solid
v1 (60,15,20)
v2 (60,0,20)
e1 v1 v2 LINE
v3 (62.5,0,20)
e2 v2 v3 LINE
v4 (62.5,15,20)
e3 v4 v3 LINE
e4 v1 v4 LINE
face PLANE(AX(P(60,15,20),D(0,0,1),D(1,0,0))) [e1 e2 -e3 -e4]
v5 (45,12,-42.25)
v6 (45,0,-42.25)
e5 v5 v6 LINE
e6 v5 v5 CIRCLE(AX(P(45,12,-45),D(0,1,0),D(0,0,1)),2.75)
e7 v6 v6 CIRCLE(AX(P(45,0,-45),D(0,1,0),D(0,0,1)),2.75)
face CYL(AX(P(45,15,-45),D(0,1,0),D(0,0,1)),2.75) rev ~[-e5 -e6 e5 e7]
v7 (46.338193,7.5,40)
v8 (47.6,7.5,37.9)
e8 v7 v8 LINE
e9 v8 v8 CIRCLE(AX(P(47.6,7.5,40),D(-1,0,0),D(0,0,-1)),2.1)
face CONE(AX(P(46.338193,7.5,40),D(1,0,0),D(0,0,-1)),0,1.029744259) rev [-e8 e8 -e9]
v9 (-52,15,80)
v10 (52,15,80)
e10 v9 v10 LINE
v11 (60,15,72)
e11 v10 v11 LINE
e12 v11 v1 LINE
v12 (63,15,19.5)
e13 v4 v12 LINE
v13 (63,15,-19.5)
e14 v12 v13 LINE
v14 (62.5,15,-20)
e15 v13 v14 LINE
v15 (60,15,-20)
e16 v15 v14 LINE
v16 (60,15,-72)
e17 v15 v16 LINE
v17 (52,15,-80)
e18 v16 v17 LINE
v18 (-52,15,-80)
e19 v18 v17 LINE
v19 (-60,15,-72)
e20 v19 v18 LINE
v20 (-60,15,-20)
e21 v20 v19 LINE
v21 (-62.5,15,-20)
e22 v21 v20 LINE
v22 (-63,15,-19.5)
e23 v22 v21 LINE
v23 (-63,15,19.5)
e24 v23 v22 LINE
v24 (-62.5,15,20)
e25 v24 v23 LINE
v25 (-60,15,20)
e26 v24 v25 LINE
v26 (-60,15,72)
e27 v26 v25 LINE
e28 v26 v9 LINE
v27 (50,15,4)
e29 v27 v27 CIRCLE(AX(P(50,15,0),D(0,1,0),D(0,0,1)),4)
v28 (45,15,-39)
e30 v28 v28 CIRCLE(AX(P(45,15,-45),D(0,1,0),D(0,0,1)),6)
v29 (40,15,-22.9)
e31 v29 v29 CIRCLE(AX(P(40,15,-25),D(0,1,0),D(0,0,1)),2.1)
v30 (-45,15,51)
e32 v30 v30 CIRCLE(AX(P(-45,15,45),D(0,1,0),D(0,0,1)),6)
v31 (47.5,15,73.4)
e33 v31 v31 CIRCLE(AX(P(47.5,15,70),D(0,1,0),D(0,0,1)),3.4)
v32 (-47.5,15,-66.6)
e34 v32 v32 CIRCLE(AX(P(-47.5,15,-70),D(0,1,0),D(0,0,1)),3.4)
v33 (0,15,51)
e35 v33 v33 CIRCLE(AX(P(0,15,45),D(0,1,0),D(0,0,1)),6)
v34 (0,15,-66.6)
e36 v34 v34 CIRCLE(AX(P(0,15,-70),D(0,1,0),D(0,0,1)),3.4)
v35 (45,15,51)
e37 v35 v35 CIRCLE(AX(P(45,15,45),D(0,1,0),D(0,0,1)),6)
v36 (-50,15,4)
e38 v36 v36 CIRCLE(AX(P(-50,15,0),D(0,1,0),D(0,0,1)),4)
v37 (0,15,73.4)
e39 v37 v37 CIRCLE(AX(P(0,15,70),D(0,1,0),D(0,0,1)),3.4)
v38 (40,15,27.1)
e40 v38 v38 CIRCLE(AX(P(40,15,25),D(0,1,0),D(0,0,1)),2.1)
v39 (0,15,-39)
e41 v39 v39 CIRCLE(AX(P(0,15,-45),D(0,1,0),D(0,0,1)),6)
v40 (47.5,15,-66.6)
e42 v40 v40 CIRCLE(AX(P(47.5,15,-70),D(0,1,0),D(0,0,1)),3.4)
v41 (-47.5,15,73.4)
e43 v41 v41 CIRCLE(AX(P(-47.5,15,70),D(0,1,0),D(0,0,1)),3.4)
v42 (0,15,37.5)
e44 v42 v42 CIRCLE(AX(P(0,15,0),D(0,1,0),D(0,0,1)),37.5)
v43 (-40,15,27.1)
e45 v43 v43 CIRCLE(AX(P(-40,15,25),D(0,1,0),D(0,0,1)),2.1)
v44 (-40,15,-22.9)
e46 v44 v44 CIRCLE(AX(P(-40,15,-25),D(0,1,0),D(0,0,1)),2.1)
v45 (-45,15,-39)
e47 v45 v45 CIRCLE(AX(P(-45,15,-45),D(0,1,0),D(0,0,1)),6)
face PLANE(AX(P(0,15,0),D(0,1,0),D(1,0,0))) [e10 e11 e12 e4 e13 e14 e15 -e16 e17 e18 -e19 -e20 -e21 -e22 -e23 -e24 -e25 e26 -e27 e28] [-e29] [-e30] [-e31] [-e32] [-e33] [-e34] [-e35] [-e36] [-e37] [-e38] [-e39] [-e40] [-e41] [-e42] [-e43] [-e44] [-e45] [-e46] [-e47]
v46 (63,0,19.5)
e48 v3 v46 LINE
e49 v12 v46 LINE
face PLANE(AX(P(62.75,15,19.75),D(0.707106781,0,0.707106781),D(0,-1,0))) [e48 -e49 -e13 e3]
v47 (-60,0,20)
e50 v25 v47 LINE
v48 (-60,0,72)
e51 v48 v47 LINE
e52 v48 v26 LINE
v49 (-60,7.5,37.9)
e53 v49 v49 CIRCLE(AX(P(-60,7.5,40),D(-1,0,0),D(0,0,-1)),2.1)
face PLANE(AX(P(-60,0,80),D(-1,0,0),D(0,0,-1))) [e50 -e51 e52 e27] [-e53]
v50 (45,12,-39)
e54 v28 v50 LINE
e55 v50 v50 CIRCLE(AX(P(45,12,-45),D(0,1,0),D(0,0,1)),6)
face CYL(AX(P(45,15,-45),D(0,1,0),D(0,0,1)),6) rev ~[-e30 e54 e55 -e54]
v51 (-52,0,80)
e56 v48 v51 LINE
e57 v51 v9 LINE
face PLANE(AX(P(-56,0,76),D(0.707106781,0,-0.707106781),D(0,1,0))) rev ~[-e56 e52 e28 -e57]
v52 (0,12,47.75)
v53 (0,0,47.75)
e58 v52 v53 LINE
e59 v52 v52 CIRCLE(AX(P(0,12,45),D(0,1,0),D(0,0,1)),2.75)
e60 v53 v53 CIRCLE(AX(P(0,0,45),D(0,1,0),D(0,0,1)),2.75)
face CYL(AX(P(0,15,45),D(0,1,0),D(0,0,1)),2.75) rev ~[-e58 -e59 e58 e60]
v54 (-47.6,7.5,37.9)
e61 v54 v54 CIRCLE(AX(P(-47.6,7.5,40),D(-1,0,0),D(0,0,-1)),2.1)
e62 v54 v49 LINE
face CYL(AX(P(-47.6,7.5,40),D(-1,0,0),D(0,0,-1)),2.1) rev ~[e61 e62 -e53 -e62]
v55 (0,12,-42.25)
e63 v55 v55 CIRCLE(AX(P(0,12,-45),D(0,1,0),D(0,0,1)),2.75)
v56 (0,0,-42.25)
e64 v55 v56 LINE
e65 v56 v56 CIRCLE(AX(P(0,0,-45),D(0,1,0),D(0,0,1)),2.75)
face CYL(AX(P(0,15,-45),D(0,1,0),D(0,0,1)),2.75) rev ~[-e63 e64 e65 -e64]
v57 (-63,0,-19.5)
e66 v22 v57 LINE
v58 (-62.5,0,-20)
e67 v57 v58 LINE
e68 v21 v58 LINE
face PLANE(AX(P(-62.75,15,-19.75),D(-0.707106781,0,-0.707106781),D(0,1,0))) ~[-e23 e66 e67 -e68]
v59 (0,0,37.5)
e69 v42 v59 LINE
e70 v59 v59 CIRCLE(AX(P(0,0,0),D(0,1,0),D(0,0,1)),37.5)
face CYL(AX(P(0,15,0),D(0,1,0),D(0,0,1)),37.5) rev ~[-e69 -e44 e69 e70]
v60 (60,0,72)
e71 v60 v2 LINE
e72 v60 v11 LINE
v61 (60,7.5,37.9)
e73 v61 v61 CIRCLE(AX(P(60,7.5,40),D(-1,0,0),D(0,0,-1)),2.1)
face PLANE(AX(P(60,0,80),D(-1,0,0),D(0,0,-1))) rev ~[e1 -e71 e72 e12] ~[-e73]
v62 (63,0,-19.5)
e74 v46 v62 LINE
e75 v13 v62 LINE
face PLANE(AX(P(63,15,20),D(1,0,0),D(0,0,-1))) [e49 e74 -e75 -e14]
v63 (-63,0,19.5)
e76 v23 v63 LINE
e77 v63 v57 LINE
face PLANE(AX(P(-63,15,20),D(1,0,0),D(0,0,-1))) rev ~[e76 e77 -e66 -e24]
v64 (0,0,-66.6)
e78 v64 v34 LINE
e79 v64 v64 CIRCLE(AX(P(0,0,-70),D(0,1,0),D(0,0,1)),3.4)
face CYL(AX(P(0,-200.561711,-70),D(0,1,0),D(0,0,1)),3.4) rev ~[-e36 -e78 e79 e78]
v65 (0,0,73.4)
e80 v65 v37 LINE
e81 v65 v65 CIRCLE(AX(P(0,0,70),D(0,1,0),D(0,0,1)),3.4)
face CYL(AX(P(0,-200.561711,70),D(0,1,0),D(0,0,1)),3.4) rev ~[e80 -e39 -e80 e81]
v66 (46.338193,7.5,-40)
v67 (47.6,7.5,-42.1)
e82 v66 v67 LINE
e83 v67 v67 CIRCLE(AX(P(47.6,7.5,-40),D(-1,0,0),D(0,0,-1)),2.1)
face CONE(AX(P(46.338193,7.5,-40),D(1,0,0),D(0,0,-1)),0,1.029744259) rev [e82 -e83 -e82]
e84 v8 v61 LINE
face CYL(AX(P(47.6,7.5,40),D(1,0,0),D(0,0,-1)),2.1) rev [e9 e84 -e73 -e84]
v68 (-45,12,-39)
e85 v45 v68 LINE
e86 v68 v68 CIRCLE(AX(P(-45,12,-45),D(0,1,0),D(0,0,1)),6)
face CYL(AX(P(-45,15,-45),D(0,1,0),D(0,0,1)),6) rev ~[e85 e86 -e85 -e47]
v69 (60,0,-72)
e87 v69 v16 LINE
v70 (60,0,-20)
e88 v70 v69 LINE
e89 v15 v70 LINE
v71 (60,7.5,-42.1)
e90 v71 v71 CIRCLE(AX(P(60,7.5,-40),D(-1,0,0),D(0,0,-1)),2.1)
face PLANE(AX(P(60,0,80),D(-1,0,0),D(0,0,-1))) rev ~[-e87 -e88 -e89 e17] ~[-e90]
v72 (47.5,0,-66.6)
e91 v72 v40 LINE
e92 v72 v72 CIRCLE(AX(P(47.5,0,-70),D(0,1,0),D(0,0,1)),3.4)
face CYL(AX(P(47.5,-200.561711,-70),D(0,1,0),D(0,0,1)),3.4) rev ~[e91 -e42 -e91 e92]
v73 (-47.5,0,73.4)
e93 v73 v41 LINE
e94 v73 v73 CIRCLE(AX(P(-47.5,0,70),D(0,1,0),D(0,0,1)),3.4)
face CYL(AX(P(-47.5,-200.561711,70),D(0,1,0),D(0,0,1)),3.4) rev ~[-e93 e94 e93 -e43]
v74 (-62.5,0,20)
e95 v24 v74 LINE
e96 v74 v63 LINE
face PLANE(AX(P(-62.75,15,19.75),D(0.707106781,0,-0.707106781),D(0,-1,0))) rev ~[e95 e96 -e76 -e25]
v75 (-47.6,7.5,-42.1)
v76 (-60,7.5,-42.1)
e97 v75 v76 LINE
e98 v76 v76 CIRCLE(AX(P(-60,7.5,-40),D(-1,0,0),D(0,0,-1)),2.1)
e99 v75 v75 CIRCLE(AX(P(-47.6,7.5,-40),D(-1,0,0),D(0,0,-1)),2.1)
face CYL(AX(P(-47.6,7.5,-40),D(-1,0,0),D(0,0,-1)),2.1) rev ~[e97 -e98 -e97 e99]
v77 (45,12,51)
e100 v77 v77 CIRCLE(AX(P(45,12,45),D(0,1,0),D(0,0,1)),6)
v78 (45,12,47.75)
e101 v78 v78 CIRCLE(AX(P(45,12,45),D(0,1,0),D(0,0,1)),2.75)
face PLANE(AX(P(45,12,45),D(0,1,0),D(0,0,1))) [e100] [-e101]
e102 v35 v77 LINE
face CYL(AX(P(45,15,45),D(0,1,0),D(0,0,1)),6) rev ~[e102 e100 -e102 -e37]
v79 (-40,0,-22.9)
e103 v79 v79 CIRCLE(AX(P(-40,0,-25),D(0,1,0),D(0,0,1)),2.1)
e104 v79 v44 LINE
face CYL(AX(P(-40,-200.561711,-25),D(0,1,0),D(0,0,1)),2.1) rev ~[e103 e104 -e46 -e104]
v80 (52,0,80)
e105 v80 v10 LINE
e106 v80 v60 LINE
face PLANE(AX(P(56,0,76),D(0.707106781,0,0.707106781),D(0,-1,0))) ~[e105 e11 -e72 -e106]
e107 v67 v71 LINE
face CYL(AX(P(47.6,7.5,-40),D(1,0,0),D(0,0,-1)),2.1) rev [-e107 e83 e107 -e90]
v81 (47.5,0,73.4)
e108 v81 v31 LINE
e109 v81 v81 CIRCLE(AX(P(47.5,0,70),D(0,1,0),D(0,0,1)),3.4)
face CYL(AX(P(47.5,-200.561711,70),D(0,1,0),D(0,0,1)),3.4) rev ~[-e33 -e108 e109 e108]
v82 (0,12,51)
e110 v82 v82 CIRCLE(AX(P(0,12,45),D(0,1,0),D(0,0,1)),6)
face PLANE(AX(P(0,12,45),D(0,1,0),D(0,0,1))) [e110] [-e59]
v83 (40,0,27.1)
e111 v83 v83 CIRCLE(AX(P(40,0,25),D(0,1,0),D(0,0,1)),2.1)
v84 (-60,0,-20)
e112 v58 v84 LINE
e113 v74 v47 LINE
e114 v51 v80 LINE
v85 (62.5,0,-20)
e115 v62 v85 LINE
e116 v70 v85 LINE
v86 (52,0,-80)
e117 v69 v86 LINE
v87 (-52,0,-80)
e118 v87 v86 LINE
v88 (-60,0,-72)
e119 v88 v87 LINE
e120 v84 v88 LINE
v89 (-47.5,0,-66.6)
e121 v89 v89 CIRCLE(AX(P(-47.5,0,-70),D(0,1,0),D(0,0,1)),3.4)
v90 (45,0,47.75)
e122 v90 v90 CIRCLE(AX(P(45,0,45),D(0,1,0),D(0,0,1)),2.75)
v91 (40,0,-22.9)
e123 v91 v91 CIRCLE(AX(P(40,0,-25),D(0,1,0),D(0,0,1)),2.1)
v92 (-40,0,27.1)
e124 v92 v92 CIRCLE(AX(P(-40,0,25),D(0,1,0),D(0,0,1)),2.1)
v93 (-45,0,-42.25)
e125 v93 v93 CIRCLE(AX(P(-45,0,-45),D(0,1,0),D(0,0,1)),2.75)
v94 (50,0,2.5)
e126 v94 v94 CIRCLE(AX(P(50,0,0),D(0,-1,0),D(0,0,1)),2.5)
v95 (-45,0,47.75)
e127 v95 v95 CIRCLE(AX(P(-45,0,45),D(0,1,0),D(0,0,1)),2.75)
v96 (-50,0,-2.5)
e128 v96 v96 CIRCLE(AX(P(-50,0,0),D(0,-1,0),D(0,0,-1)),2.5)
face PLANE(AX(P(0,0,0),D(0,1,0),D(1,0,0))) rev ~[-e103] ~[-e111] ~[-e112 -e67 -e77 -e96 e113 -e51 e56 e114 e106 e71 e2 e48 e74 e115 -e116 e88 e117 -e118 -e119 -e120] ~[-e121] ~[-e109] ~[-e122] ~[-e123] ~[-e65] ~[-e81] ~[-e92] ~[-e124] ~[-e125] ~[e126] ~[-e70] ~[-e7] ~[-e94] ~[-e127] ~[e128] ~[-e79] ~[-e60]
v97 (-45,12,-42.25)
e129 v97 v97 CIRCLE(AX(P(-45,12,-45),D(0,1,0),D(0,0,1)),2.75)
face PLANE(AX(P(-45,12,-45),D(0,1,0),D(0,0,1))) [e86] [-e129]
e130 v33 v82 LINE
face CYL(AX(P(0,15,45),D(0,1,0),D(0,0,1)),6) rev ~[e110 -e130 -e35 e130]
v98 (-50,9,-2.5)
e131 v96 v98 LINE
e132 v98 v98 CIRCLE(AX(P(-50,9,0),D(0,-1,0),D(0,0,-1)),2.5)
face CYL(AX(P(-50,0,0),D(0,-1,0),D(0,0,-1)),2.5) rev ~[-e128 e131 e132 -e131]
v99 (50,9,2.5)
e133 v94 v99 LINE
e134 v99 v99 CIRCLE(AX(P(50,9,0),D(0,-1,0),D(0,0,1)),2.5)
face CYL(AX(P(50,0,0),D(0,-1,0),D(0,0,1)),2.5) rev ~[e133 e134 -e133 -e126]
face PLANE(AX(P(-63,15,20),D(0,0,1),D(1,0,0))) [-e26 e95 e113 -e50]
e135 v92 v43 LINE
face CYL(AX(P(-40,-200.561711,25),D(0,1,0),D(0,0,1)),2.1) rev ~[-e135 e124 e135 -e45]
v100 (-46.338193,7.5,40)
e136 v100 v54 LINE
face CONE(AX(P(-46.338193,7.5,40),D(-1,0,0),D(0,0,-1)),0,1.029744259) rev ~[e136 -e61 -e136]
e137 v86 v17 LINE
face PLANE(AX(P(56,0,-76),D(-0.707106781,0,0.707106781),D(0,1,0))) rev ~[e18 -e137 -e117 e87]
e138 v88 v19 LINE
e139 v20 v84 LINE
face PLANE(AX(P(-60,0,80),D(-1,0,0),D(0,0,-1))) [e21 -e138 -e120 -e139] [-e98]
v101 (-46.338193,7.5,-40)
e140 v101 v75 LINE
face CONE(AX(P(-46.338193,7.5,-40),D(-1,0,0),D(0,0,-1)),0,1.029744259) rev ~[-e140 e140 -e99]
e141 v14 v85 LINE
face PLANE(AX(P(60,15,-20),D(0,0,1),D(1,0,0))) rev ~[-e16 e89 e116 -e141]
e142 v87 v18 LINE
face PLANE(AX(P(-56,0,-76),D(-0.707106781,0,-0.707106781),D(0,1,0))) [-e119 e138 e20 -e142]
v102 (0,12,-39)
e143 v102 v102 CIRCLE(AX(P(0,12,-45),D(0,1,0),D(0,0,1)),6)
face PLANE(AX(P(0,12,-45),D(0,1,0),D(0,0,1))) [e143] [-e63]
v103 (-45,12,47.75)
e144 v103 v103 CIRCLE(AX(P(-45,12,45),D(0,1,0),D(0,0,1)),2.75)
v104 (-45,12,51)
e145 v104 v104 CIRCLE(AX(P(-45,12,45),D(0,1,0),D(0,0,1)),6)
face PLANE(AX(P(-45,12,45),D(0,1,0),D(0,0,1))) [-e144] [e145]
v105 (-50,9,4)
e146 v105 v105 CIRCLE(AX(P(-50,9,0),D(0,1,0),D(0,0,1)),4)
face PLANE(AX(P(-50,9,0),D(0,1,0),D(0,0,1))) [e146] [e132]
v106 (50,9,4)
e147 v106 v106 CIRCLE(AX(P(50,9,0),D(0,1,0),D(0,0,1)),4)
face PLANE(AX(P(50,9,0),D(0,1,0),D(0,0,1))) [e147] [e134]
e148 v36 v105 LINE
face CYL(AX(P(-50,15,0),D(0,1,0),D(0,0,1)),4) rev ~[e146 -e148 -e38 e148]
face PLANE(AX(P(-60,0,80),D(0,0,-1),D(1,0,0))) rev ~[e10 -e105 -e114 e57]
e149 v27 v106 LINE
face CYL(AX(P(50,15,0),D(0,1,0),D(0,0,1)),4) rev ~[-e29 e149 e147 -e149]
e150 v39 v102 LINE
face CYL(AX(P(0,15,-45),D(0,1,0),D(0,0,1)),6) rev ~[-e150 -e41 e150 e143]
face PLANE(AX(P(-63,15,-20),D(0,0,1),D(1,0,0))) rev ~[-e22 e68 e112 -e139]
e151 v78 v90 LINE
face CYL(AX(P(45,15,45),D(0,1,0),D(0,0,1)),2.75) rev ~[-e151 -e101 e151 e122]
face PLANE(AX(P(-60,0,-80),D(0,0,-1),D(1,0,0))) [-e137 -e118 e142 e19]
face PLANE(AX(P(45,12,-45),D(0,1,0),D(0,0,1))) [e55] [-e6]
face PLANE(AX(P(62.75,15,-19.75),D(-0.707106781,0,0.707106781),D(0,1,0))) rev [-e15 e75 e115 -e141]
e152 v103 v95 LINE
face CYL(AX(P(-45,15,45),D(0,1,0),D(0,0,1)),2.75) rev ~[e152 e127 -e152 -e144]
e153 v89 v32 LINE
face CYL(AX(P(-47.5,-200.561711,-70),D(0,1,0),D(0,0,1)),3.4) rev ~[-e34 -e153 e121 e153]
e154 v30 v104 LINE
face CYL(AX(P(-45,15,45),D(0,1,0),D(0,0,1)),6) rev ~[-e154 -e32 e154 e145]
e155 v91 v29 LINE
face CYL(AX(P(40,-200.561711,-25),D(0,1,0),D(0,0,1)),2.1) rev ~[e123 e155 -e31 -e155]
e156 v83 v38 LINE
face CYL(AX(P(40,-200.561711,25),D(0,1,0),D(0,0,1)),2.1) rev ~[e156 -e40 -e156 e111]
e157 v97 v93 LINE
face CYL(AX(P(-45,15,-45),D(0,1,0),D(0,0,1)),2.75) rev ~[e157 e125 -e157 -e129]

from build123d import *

# Parameters (mm, degrees)
SKETCH1_W                  = 120
SKETCH1_H                  = 160
BOSS_EXTRUDE1_DEPTH        = 15
CHAMFER1_SIZE              = 8
SKETCH2_R                  = 37.5
CUT_EXTRUDE1_DEPTH         = 23
SKETCH3_R                  = 1
CUT_EXTRUDE2_DEPTH         = 10
M5_TAPPED_HOLE1_D          = 4.2
SKETCH8_R                  = 3
CUT_EXTRUDE4_DEPTH         = 55
M8_TAPPED_HOLE1_D          = 6.8
SKETCH11_R                 = 2.5
CUT_EXTRUDE5_DEPTH         = 33
SKETCH12_R                 = 4
CUT_EXTRUDE6_DEPTH         = 6
SKETCH13_W                 = 3
SKETCH13_H                 = 40
BOSS_EXTRUDE2_DEPTH        = 15
CHAMFER2_SIZE              = 0.5
SKETCH14_R                 = 1.794169989
SKETCH14_R_2               = 1.756446965
CUT_EXTRUDE7_DEPTH         = 5
M5_TAPPED_HOLE2_AT_2_COUNT = 2
M5_TAPPED_HOLE2_AT_2_PITCH = 80
SKETCH16_R                 = 2.75
CUT_EXTRUDE8_DEPTH         = 55
SKETCH17_R                 = 6
CUT_EXTRUDE9_DEPTH         = 3


with BuildPart() as part:
    # Sketch1 → Boss-Extrude1 (new body)
    with BuildSketch(Plane(origin=(0, 0, 0), x_dir=(1, 0, 0), z_dir=(0, 1, 0))):
        Rectangle(SKETCH1_W, SKETCH1_H)
    extrude(amount=BOSS_EXTRUDE1_DEPTH)

    # Chamfer1
    chamfer1_edges = [part.edges().sort_by_distance(p)[0] for p in [
        (60, 7.5, 80),
        (-60, 7.5, 80),
        (-60, 7.5, -80),
        (60, 7.5, -80),
    ]]
    chamfer(chamfer1_edges, length=CHAMFER1_SIZE)

    # Sketch2 → Cut-Extrude1 (cut)
    with BuildSketch(Plane(origin=(0, 15, 0), x_dir=(1, 0, 0), z_dir=(0, 1, 0))):
        with Locations(Location((0, 0, 0), (0, 0, 270))):
            Circle(SKETCH2_R)
    extrude(amount=-CUT_EXTRUDE1_DEPTH, mode=Mode.SUBTRACT)

    # Sketch3 → Cut-Extrude2 (cut)
    with BuildSketch(Plane.XZ):
        with Locations(Location((-40, 25, 0), (0, 0, 270))):
            Circle(SKETCH3_R)
        with Locations(Location((40, 25, 0), (0, 0, 90))):
            Circle(SKETCH3_R)
        with Locations(Location((-40, -25, 0), (0, 0, 90))):
            Circle(SKETCH3_R)
        with Locations(Location((40, -25, 0), (0, 0, 270))):
            Circle(SKETCH3_R)
    extrude(amount=-CUT_EXTRUDE2_DEPTH, mode=Mode.SUBTRACT)

    # M5 Tapped Hole1 (through all)
    with Locations(Plane(origin=(-40, 0, 25), x_dir=(0, 0, -1), z_dir=(0, -1, 0))):
        with Locations((0, 0), (0, 80), (50, 80), (50, 0)):
            Hole(M5_TAPPED_HOLE1_D / 2)

    # Sketch8 → Cut-Extrude4 (cut)
    with BuildSketch(Plane.XZ):
        with Locations(Location((-47.5, 70, 0), (0, 0, 270))):
            Circle(SKETCH8_R)
        with Locations(Location((0, 70, 0), (0, 0, 270))):
            Circle(SKETCH8_R)
        with Locations(Location((47.5, 70, 0), (0, 0, 90))):
            Circle(SKETCH8_R)
        with Locations(Location((47.5, -70, 0), (0, 0, 270))):
            Circle(SKETCH8_R)
        with Locations(Location((0, -70, 0), (0, 0, 90))):
            Circle(SKETCH8_R)
        with Locations(Location((-47.5, -70, 0), (0, 0, 90))):
            Circle(SKETCH8_R)
    extrude(amount=-CUT_EXTRUDE4_DEPTH, mode=Mode.SUBTRACT)

    # M8 Tapped Hole1 (through all)
    with Locations(Plane(origin=(47.5, 0, -70), x_dir=(0, 0, -1), z_dir=(0, -1, 0))):
        with Locations((0, 0), (0, -47.5), (0, -95), (-140, -95), (-140, -47.5), (-140, 0)):
            Hole(M8_TAPPED_HOLE1_D / 2)

    # Sketch11 → Cut-Extrude5 (cut)
    with BuildSketch(Plane.XZ):
        with Locations(Location((-50, 0, 0), (0, 0, 270))):
            Circle(SKETCH11_R)
        with Locations(Location((50, 0, 0), (0, 0, 90))):
            Circle(SKETCH11_R)
    extrude(amount=-CUT_EXTRUDE5_DEPTH, mode=Mode.SUBTRACT)

    # Sketch12 → Cut-Extrude6 (cut)
    with BuildSketch(Plane(origin=(0, 15, 0), x_dir=(1, 0, 0), z_dir=(0, 1, 0))):
        with Locations(Location((-50, 0, 0), (0, 0, 270))):
            Circle(SKETCH12_R)
        with Locations(Location((50, 0, 0), (0, 0, 270))):
            Circle(SKETCH12_R)
    extrude(amount=-CUT_EXTRUDE6_DEPTH, mode=Mode.SUBTRACT)

    # Sketch13 → Boss-Extrude2 (add)
    with BuildSketch(Plane(origin=(0, 15, 0), x_dir=(1, 0, 0), z_dir=(0, 1, 0))):
        with Locations((-61.5, 0)):
            Rectangle(SKETCH13_W, SKETCH13_H)
        with Locations((61.5, 0)):
            Rectangle(SKETCH13_W, SKETCH13_H)
    extrude(amount=-BOSS_EXTRUDE2_DEPTH)

    # Chamfer2
    chamfer2_edges = [part.edges().sort_by_distance(p)[0] for p in [
        (63, 7.5, -20),
        (63, 7.5, 20),
        (-63, 7.5, -20),
        (-63, 7.5, 20),
    ]]
    chamfer(chamfer2_edges, length=CHAMFER2_SIZE)

    # Sketch14 → Cut-Extrude7 (cut)
    with BuildSketch(Plane(origin=(60, 0, 0), x_dir=(0, 0, -1), z_dir=(1, 0, 0))):
        with Locations((-40, 7.5)):
            Circle(SKETCH14_R)
        with Locations((40, 7.5)):
            Circle(SKETCH14_R_2)
    extrude(amount=-CUT_EXTRUDE7_DEPTH, mode=Mode.SUBTRACT)

    # Sketch15 → M5 Tapped Hole2 (revolve, cut)
    with BuildSketch(Plane(origin=(60, 7.5, 40), x_dir=(0, 0, -1), z_dir=(0, 1, 0))):
        Polygon((0, 0), (0, 13.6618073), (2.1, 12.4), (2.1, 0), align=None)
    m5_tapped_hole2 = revolve(axis=Axis((66.35, 7.5, 40), (-1, 0, 0)), mode=Mode.SUBTRACT)

    # M5 Tapped Hole2 at 2: M5 Tapped Hole2 ×2
    with Locations(*[(0, 0, -i * M5_TAPPED_HOLE2_AT_2_PITCH) for i in range(1, M5_TAPPED_HOLE2_AT_2_COUNT)]):
        add(m5_tapped_hole2, mode=Mode.SUBTRACT)

    # Mirror1: M5 Tapped Hole2 across plane
    add(m5_tapped_hole2.mirror(Plane(origin=(0, 0, 0), x_dir=(0, 0, 1), z_dir=(1, 0, 0))), mode=Mode.SUBTRACT)

    # Mirror1 copy 1 sketch → Mirror1 copy 1 (revolve, cut)
    with BuildSketch(Plane(origin=(-60, 7.5, -40), x_dir=(0, 0, -1), z_dir=(0, 1, 0))):
        Polygon((0, 0), (0, -13.6618073), (2.1, -12.4), (2.1, 0), align=None)
    revolve(axis=Axis((-66.35, 7.5, -40), (-1, 0, 0)), mode=Mode.SUBTRACT)

    # Sketch16 → Cut-Extrude8 (cut)
    with BuildSketch(Plane(origin=(0, 15, 0), x_dir=(1, 0, 0), z_dir=(0, 1, 0))):
        with Locations(Location((0, 45, 0), (0, 0, 270))):
            Circle(SKETCH16_R)
        with Locations(Location((45, 45, 0), (0, 0, 270))):
            Circle(SKETCH16_R)
        with Locations(Location((-45, 45, 0), (0, 0, 270))):
            Circle(SKETCH16_R)
        with Locations(Location((-45, -45, 0), (0, 0, 270))):
            Circle(SKETCH16_R)
        with Locations(Location((45, -45, 0), (0, 0, 270))):
            Circle(SKETCH16_R)
        with Locations(Location((0, -45, 0), (0, 0, 270))):
            Circle(SKETCH16_R)
    extrude(amount=-CUT_EXTRUDE8_DEPTH, mode=Mode.SUBTRACT)

    # Sketch17 → Cut-Extrude9 (cut)
    with BuildSketch(Plane(origin=(0, 15, 0), x_dir=(1, 0, 0), z_dir=(0, 1, 0))):
        with Locations(Location((-45, -45, 0), (0, 0, 270))):
            Circle(SKETCH17_R)
        with Locations(Location((0, -45, 0), (0, 0, 270))):
            Circle(SKETCH17_R)
        with Locations(Location((45, -45, 0), (0, 0, 270))):
            Circle(SKETCH17_R)
        with Locations(Location((0, 45, 0), (0, 0, 270))):
            Circle(SKETCH17_R)
        with Locations(Location((45, 45, 0), (0, 0, 270))):
            Circle(SKETCH17_R)
        with Locations(Location((-45, 45, 0), (0, 0, 270))):
            Circle(SKETCH17_R)
    extrude(amount=-CUT_EXTRUDE9_DEPTH, mode=Mode.SUBTRACT)


solid = part.part
